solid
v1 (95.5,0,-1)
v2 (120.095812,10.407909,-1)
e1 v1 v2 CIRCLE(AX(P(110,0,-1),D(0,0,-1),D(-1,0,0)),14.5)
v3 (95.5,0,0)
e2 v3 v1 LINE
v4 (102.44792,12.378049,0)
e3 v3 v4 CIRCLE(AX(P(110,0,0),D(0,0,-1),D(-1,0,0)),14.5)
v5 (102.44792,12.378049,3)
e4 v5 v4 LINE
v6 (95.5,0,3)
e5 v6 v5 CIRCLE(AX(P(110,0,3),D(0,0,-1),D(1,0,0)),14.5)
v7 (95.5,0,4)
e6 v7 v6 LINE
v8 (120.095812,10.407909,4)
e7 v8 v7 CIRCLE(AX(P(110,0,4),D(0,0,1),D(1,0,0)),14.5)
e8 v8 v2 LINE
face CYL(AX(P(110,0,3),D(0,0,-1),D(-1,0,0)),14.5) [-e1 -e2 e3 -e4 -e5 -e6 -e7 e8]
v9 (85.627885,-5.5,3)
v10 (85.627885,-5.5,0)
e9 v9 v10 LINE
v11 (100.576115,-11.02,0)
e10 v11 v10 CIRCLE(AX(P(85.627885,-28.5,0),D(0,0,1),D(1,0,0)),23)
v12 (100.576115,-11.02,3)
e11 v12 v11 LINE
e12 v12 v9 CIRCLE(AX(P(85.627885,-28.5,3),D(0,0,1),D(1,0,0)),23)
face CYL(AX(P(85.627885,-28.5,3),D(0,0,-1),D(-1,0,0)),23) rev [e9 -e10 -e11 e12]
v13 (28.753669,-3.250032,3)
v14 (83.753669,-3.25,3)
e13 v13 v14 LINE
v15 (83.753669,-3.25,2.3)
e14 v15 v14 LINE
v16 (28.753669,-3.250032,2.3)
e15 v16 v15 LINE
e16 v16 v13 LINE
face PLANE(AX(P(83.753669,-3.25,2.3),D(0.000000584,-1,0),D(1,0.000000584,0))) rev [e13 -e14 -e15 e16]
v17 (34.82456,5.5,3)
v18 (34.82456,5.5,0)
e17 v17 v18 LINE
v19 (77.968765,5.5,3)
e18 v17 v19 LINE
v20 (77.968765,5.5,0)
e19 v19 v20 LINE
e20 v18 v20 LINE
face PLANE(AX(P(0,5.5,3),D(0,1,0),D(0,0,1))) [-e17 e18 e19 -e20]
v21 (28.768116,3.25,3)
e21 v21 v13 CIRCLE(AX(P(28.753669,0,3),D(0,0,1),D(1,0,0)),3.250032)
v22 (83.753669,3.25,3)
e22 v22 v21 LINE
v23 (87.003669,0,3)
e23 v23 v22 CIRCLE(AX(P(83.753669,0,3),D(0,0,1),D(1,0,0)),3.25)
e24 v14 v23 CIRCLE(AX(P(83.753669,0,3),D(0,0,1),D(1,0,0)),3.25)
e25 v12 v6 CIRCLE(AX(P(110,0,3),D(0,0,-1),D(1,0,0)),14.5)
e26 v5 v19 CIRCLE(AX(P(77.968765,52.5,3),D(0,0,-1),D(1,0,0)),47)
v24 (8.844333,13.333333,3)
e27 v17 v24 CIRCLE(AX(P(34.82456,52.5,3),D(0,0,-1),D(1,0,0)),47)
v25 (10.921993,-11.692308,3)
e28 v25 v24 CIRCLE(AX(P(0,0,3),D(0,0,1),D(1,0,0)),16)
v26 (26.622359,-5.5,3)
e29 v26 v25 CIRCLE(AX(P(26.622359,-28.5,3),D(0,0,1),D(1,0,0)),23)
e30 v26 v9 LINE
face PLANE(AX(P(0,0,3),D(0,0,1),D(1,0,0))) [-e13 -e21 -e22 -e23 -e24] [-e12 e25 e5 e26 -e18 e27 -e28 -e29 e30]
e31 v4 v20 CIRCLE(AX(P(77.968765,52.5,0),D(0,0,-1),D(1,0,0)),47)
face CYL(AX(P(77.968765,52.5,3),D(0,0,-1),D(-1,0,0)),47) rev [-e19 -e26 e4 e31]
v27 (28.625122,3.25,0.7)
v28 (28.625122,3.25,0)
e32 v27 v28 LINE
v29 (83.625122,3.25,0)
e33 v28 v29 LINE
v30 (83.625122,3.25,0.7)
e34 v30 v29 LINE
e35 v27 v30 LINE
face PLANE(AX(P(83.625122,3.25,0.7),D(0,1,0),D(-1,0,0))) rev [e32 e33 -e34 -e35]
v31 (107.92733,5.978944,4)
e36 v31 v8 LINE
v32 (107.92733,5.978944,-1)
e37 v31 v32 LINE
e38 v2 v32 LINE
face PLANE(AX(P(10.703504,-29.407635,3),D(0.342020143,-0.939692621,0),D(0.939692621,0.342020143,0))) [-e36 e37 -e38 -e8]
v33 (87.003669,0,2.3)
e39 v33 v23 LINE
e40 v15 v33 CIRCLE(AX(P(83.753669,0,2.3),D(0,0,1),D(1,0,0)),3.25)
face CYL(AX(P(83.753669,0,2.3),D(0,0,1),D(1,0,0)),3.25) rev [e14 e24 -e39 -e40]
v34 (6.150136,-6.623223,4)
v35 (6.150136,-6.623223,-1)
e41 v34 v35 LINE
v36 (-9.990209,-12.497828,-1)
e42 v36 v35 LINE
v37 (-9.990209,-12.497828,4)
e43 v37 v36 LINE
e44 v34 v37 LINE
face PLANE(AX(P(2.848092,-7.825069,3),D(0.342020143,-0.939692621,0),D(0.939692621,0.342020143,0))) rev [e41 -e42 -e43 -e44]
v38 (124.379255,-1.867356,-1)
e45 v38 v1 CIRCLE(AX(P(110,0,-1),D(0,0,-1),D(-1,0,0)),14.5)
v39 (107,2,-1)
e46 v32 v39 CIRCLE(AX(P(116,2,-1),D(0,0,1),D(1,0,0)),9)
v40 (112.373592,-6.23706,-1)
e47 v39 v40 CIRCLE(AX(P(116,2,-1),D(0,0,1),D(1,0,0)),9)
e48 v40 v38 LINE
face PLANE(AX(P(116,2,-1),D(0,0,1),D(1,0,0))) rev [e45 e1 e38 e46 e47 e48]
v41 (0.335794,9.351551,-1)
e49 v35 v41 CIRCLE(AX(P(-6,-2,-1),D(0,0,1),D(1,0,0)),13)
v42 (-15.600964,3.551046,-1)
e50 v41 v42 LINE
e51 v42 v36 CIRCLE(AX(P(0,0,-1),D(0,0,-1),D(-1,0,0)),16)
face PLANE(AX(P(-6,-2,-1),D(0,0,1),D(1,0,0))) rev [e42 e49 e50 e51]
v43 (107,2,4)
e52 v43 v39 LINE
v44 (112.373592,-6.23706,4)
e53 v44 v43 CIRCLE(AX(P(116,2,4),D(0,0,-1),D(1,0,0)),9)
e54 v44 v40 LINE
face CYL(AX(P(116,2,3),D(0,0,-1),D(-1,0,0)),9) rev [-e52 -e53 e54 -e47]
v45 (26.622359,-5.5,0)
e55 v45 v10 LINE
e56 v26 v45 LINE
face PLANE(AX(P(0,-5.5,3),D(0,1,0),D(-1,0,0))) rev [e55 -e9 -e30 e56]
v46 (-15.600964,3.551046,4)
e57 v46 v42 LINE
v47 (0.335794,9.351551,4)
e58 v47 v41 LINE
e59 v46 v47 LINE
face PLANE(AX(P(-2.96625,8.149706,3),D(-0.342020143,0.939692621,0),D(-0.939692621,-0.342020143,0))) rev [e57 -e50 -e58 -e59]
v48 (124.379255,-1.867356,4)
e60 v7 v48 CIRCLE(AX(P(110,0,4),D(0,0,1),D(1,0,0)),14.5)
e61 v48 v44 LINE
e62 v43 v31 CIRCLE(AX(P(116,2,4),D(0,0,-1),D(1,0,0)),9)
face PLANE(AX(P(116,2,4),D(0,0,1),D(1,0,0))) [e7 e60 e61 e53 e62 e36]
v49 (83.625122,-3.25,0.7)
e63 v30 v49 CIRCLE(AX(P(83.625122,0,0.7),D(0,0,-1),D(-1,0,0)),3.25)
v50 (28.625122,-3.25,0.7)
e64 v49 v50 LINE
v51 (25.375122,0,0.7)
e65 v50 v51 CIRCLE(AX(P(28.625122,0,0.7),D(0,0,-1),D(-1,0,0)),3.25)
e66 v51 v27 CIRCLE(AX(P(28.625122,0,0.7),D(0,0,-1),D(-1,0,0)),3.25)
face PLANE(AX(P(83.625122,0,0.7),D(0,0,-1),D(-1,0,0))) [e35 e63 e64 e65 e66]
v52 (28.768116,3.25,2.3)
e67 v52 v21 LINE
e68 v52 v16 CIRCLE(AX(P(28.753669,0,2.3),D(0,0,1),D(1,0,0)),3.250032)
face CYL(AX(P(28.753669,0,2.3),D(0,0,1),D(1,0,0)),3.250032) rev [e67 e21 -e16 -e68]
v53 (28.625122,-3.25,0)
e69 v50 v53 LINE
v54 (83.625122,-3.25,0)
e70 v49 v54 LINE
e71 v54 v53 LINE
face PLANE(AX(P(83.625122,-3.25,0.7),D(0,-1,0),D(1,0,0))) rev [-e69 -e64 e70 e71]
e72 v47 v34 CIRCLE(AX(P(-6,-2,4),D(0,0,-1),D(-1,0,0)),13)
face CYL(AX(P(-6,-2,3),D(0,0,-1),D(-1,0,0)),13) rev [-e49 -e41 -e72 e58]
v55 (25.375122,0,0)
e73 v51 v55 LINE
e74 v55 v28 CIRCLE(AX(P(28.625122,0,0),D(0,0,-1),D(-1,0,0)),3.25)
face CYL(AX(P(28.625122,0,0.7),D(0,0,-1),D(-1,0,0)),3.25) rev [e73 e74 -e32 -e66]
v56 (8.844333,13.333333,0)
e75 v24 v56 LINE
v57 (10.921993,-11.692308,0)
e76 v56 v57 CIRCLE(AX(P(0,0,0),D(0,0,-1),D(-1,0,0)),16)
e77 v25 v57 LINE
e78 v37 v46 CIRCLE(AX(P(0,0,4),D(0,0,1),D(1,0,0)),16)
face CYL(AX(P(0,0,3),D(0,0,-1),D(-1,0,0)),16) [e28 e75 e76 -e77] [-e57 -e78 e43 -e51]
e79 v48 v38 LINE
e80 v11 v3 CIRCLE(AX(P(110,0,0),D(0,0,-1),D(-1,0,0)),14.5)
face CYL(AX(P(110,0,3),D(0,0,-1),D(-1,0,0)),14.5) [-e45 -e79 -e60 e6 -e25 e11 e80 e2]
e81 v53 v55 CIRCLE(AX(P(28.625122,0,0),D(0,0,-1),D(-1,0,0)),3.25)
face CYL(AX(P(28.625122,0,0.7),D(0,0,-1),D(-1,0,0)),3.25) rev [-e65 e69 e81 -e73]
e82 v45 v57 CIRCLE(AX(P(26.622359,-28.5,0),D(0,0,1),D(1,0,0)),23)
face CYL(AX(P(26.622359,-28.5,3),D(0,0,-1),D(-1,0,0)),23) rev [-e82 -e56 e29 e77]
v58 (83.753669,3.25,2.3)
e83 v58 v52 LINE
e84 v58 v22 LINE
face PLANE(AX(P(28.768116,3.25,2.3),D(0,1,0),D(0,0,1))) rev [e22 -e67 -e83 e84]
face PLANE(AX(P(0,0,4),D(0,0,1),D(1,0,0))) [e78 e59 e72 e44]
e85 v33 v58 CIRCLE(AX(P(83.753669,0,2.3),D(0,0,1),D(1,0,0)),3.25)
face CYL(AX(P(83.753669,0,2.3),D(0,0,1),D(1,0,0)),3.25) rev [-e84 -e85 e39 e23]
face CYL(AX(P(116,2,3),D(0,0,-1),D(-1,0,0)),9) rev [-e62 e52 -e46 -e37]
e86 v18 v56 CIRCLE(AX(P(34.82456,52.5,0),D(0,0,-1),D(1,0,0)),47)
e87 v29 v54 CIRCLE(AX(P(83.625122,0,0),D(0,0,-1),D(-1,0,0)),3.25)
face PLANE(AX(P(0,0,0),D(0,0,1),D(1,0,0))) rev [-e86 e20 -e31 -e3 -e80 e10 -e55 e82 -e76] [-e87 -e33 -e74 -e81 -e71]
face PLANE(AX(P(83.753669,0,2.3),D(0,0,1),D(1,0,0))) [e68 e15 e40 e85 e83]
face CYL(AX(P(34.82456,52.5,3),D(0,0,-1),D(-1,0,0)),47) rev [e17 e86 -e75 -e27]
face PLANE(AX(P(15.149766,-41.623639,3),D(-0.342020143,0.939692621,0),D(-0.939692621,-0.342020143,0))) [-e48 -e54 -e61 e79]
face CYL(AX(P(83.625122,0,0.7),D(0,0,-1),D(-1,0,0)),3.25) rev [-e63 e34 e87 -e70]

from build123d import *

# Parameters (mm, degrees)
SPANNER_BODY_3MM_DEPTH          = 3
HEAD_PAD_13_SIDE_A_DEPTH        = 1
HEAD_START                      = 1
HEAD_PAD_13_SIDE_B_DEPTH        = 1
HEAD_PAD_9_SIDE_A_DEPTH         = 1
HEAD_PAD_9_SIDE_B_DEPTH         = 1
HANDLE_SLOT_SIDE_A_55X6_5_DEPTH = 0.7
HANDLE_SLOT_SIDE_B_55X6_5_DEPTH = 0.7


with BuildPart() as part:
    # Spanner Profile Sketch → Spanner Body 3mm (new body)
    with BuildSketch(Plane.XY):
        with BuildLine():
            ThreePointArc((0.335793671, 9.351551373), (4.669621374, 5.426922629), (6.845232579, 0))
            Line((6.845232579, 0), (107.225035612, 0))
            ThreePointArc((107.225035612, 0), (107.061451957, 3.049932803), (107.927329677, 5.978943813))
            Line((107.927329677, 5.978943813), (120.095812241, 10.407909262))
            ThreePointArc((120.095812241, 10.407909262), (111.608728128, 14.410482081), (102.447920261, 12.37804878))
            ThreePointArc((102.447920261, 12.37804878), (90.682307093, 7.25217294), (77.968765244, 5.5))
            Line((77.968765244, 5.5), (34.824560299, 5.5))
            ThreePointArc((34.824560299, 5.5), (21.256828973, 7.500925935), (8.844332774, 13.333333333))
            ThreePointArc((8.844332774, 13.333333333), (-5.944434547, 14.854753378), (-15.600963823, 3.551046014))
            Line((-15.600963823, 3.551046014), (0.335793671, 9.351551373))
        make_face()
        with BuildLine():
            Line((107.225035612, 0), (6.845232579, 0))
            ThreePointArc((6.845232579, 0), (6.928993977, -3.356876833), (6.150136107, -6.623223181))
            Line((6.150136107, -6.623223181), (-9.990209349, -12.497828498))
            ThreePointArc((-9.990209349, -12.497828498), (0.615850097, -15.988143377), (10.921993446, -11.692307692))
            ThreePointArc((10.921993446, -11.692307692), (18.183666088, -7.104008283), (26.622359024, -5.5))
            Line((26.622359024, -5.5), (85.627884786, -5.5))
            ThreePointArc((85.627884786, -5.5), (93.595318501, -6.924087505), (100.576115451, -11.02))
            ThreePointArc((100.576115451, -11.02), (115.204003038, -13.533970311), (124.379255248, -1.867356026))
            Line((124.379255248, -1.867356026), (112.37359154, -6.237060258))
            ThreePointArc((112.37359154, -6.237060258), (109.059269326, -3.729420365), (107.225035612, 0))
        make_face()
    extrude(amount=SPANNER_BODY_3MM_DEPTH)

    # Head Pad 13 Side A Sketch → Head Pad 13 Side A (add)
    with BuildSketch(Plane.XY.offset(3)):
        with BuildLine():
            Line((-15.600963823, 3.551046014), (0.335793671, 9.351551373))
            ThreePointArc((0.335793671, 9.351551373), (6.21600407, 2.446261863), (6.150136107, -6.623223181))
            Line((6.150136107, -6.623223181), (-9.990209349, -12.497828498))
            ThreePointArc((-9.990209349, -12.497828498), (15.10359657, 5.280281303), (-15.600963823, 3.551046014))
        make_face()
    extrude(amount=HEAD_PAD_13_SIDE_A_DEPTH)

    # Head Pad 13 Side B Sketch → Head Pad 13 Side B (add)
    with BuildSketch(Plane(origin=(0, 0, 0), x_dir=(-1, 0, 0), z_dir=(0, 0, -1)).offset(HEAD_START)):
        with BuildLine():
            Line((-0.335793671, 9.351551373), (15.600963823, 3.551046014))
            ThreePointArc((15.600963823, 3.551046014), (-15.10359657, 5.280281303), (9.990209349, -12.497828498))
            Line((9.990209349, -12.497828498), (-6.150136107, -6.623223181))
            ThreePointArc((-6.150136107, -6.623223181), (-6.21600407, 2.446261863), (-0.335793671, 9.351551373))
        make_face()
    extrude(amount=-HEAD_PAD_13_SIDE_B_DEPTH)

    # Head Pad 9 Side A Sketch → Head Pad 9 Side A (add)
    with BuildSketch(Plane(origin=(0, 0, 0), x_dir=(-1, 0, 0), z_dir=(0, 0, -1)).offset(HEAD_START)):
        with BuildLine():
            Line((-107.927329677, 5.978943813), (-120.095812241, 10.407909262))
            ThreePointArc((-120.095812241, 10.407909262), (-96.309573907, -4.777262123), (-124.379255248, -1.867356026))
            Line((-124.379255248, -1.867356026), (-112.37359154, -6.237060258))
            ThreePointArc((-112.37359154, -6.237060258), (-107.542766412, -1.07818129), (-107.927329677, 5.978943813))
        make_face()
    extrude(amount=-HEAD_PAD_9_SIDE_A_DEPTH)

    # Head Pad 9 Side B Sketch → Head Pad 9 Side B (add)
    with BuildSketch(Plane.XY.offset(3)):
        with BuildLine():
            Line((107.927329677, 5.978943813), (120.095812241, 10.407909262))
            ThreePointArc((120.095812241, 10.407909262), (96.309573907, -4.777262123), (124.379255248, -1.867356026))
            Line((124.379255248, -1.867356026), (112.37359154, -6.237060258))
            ThreePointArc((112.37359154, -6.237060258), (107.542766412, -1.07818129), (107.927329677, 5.978943813))
        make_face()
    extrude(amount=HEAD_PAD_9_SIDE_B_DEPTH)

    # Handle Slot Side A Sketch → Handle Slot Side A 55x6.5 (cut)
    with BuildSketch(Plane.XY.offset(3)):
        with BuildLine():
            Line((28.768116085, 3.25), (83.753668591, 3.25))
            ThreePointArc((83.753668591, 3.25), (87.003668591, 0), (83.753668591, -3.25))
            Line((83.753668591, -3.25), (28.753668591, -3.250032112))
            ThreePointArc((28.753668591, -3.250032112), (25.503644507, 0.007223765), (28.768116085, 3.25))
        make_face()
    extrude(amount=-HANDLE_SLOT_SIDE_A_55X6_5_DEPTH, mode=Mode.SUBTRACT)

    # Handle Slot Side B Sketch → Handle Slot Side B 55x6.5 (cut)
    with BuildSketch(Plane(origin=(0, 0, 0), x_dir=(-1, 0, 0), z_dir=(0, 0, -1))):
        with BuildLine():
            Line((-83.625121905, 3.25), (-28.625121905, 3.25))
            ThreePointArc((-28.625121905, 3.25), (-25.375121905, 0), (-28.625121905, -3.25))
            Line((-28.625121905, -3.25), (-83.625121905, -3.25))
            ThreePointArc((-83.625121905, -3.25), (-86.875121905, 0), (-83.625121905, 3.25))
        make_face()
    extrude(amount=-HANDLE_SLOT_SIDE_B_55X6_5_DEPTH, mode=Mode.SUBTRACT)


solid = part.part
